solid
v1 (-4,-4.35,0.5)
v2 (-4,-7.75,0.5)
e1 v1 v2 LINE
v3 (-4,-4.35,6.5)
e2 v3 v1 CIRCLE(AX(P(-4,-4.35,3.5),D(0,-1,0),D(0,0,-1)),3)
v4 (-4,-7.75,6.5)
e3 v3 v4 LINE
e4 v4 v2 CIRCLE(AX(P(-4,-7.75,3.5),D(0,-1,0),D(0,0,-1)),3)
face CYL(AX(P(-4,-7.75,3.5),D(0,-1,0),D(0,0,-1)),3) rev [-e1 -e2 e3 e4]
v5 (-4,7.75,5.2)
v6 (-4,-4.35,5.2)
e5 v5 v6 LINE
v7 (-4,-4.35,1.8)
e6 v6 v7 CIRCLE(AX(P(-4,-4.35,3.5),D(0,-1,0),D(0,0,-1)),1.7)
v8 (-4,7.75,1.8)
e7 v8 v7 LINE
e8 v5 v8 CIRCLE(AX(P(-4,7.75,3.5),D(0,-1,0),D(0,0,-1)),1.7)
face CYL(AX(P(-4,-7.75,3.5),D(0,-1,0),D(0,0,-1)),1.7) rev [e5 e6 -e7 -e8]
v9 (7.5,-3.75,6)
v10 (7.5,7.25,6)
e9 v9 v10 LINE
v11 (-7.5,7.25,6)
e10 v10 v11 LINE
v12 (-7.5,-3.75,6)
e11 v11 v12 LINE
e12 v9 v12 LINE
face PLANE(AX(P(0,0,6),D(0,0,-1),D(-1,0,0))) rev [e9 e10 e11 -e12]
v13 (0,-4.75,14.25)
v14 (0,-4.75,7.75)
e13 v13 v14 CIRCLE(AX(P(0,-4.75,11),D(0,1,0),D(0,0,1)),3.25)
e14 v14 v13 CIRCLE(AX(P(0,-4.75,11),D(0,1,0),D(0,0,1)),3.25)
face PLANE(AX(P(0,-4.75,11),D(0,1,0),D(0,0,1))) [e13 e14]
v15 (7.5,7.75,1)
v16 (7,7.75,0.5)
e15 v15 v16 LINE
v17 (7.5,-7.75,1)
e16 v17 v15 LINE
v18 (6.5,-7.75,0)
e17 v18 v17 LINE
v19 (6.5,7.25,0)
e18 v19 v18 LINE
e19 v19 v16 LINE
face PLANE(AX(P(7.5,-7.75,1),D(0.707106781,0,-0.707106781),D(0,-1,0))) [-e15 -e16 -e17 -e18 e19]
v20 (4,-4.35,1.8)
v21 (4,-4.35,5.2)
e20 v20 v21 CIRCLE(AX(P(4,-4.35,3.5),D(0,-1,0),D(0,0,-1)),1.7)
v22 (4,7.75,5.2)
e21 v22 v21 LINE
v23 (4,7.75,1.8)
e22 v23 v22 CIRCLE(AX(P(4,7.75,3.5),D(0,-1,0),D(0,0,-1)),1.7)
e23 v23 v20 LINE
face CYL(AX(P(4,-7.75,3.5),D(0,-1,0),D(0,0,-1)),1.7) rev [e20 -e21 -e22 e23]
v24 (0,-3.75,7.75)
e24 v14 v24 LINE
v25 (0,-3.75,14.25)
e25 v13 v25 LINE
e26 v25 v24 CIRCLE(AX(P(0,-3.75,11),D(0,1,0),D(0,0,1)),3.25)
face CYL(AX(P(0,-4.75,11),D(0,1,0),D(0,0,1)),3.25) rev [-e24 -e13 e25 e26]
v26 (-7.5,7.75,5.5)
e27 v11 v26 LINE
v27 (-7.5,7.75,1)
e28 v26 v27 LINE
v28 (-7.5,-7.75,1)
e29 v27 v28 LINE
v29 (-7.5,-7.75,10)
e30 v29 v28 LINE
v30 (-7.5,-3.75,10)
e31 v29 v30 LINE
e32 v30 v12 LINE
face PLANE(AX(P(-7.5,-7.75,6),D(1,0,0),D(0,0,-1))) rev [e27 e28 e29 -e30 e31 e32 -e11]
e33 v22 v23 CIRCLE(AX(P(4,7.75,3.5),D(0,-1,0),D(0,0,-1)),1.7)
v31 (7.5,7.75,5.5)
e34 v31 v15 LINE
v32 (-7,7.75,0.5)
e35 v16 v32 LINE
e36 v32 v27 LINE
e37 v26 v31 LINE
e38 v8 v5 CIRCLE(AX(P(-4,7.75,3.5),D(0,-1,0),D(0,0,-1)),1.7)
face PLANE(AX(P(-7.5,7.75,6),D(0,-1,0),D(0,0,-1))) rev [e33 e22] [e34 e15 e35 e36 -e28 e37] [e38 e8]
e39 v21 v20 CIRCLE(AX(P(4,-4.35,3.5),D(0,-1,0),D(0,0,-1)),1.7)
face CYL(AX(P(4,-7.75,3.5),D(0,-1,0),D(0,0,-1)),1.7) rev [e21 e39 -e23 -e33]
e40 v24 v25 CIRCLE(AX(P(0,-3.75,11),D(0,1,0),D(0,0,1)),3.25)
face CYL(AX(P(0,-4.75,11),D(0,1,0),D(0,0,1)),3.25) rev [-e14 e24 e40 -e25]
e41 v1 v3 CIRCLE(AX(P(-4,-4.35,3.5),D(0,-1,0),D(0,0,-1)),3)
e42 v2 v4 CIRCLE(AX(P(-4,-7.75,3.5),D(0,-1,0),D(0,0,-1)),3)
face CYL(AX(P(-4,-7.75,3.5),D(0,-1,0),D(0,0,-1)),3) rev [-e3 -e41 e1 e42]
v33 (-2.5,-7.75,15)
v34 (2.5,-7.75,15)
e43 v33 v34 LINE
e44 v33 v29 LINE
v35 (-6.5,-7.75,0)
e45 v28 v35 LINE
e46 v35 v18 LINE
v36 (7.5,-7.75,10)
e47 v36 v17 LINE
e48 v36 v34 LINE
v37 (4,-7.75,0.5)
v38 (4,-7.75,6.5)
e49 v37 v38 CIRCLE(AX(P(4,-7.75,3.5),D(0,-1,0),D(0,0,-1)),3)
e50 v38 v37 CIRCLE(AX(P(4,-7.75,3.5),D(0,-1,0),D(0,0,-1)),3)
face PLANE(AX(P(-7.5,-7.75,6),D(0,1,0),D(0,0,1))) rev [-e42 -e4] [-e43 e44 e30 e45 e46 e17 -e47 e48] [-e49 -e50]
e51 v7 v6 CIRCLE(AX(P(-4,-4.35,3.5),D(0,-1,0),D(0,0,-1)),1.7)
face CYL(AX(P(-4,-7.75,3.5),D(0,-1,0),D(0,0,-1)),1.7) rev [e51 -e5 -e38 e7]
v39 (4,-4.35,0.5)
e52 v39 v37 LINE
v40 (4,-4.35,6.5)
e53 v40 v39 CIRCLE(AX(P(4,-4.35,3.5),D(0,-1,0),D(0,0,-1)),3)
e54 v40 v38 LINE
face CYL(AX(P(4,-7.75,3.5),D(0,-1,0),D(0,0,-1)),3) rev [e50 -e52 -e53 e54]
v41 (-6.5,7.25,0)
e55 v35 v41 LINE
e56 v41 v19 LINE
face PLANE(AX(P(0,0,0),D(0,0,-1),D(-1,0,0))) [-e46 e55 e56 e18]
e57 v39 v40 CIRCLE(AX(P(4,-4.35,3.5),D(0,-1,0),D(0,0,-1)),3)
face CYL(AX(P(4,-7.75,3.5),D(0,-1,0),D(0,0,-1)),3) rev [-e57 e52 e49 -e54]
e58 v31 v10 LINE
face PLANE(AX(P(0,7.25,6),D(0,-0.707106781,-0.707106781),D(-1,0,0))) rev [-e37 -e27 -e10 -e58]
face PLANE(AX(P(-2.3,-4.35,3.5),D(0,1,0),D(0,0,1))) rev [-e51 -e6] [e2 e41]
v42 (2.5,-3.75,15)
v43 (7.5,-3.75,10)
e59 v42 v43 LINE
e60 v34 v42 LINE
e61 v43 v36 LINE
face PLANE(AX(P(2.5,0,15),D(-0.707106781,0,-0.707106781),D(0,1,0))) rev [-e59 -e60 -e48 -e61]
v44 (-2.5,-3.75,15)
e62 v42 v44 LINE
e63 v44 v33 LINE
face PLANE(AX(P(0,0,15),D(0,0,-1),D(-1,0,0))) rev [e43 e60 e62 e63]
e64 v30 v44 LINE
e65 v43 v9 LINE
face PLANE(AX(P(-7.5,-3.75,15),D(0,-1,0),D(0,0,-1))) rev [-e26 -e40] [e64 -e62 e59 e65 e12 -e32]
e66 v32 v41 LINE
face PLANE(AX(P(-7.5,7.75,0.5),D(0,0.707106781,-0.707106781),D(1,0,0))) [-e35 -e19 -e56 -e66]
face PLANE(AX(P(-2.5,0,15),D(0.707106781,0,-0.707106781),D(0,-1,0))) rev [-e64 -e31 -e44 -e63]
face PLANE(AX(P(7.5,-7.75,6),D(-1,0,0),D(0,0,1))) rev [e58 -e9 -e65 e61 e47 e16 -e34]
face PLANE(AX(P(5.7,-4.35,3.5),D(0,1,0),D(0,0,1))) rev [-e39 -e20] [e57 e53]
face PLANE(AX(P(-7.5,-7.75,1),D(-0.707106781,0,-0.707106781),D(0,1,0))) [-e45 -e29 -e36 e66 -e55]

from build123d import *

# Parameters (mm, degrees)
SKETCH1_W                                            = 15
SKETCH1_H                                            = 15.5
BOSS_EXTRUDE1_DEPTH                                  = 6
SKETCH2_W                                            = 15
SKETCH2_H                                            = 4
BOSS_EXTRUDE2_DEPTH                                  = 9
SKETCH3_R                                            = 3.25
CUT_EXTRUDE1_DEPTH                                   = 1
HOLE_SIZE_PER_SOCKET_HEAD_CAP_SCREW_TYPE_D           = 3.4
HOLE_SIZE_PER_SOCKET_HEAD_CAP_SCREW_TYPE_CBORE_D     = 6
HOLE_SIZE_PER_SOCKET_HEAD_CAP_SCREW_TYPE_CBORE_DEPTH = 3.4
CHAMFER1_SIZE                                        = 5
CHAMFER2_SIZE                                        = 1
CHAMFER3_SIZE                                        = 0.5


with BuildPart() as part:
    # Sketch1 → Boss-Extrude1 (new body)
    with BuildSketch(Plane.XY):
        Rectangle(SKETCH1_W, SKETCH1_H)
    extrude(amount=BOSS_EXTRUDE1_DEPTH)

    # Sketch2 → Boss-Extrude2 (add)
    with BuildSketch(Plane.XY.offset(6)):
        with Locations((0, -5.75)):
            Rectangle(SKETCH2_W, SKETCH2_H)
    extrude(amount=BOSS_EXTRUDE2_DEPTH)

    # Sketch3 → Cut-Extrude1 (cut)
    with BuildSketch(Plane(origin=(0, -3.75, 0), x_dir=(1, 0, 0), z_dir=(0, 1, 0))):
        with Locations(Location((0, -11, 0), (0, 0, 270))):
            Circle(SKETCH3_R)
    extrude(amount=-CUT_EXTRUDE1_DEPTH, mode=Mode.SUBTRACT)

    # Hole size per socket head cap screw type 1 (through all)
    with Locations(Plane(origin=(0, -7.75, 0), x_dir=(-1, 0, 0), z_dir=(0, -1, 0))):
        with Locations((4, -3.5), (-4, -3.5)):
            CounterBoreHole(HOLE_SIZE_PER_SOCKET_HEAD_CAP_SCREW_TYPE_D / 2, HOLE_SIZE_PER_SOCKET_HEAD_CAP_SCREW_TYPE_CBORE_D / 2, HOLE_SIZE_PER_SOCKET_HEAD_CAP_SCREW_TYPE_CBORE_DEPTH)

    # Chamfer1
    chamfer1_edges = [part.edges().sort_by_distance(p)[0] for p in [
        (-7.5, -5.75, 15),
        (7.5, -5.75, 15),
    ]]
    chamfer(chamfer1_edges, length=CHAMFER1_SIZE)

    # Chamfer2
    chamfer2_edges = [part.edges().sort_by_distance(p)[0] for p in [
        (-7.5, 0, 0),
        (7.5, 0, 0),
    ]]
    chamfer(chamfer2_edges, length=CHAMFER2_SIZE)

    # Chamfer3
    chamfer3_edges = [part.edges().sort_by_distance(p)[0] for p in [
        (0, 7.75, 6),
        (0, 7.75, 0),
    ]]
    chamfer(chamfer3_edges, length=CHAMFER3_SIZE)


solid = part.part
